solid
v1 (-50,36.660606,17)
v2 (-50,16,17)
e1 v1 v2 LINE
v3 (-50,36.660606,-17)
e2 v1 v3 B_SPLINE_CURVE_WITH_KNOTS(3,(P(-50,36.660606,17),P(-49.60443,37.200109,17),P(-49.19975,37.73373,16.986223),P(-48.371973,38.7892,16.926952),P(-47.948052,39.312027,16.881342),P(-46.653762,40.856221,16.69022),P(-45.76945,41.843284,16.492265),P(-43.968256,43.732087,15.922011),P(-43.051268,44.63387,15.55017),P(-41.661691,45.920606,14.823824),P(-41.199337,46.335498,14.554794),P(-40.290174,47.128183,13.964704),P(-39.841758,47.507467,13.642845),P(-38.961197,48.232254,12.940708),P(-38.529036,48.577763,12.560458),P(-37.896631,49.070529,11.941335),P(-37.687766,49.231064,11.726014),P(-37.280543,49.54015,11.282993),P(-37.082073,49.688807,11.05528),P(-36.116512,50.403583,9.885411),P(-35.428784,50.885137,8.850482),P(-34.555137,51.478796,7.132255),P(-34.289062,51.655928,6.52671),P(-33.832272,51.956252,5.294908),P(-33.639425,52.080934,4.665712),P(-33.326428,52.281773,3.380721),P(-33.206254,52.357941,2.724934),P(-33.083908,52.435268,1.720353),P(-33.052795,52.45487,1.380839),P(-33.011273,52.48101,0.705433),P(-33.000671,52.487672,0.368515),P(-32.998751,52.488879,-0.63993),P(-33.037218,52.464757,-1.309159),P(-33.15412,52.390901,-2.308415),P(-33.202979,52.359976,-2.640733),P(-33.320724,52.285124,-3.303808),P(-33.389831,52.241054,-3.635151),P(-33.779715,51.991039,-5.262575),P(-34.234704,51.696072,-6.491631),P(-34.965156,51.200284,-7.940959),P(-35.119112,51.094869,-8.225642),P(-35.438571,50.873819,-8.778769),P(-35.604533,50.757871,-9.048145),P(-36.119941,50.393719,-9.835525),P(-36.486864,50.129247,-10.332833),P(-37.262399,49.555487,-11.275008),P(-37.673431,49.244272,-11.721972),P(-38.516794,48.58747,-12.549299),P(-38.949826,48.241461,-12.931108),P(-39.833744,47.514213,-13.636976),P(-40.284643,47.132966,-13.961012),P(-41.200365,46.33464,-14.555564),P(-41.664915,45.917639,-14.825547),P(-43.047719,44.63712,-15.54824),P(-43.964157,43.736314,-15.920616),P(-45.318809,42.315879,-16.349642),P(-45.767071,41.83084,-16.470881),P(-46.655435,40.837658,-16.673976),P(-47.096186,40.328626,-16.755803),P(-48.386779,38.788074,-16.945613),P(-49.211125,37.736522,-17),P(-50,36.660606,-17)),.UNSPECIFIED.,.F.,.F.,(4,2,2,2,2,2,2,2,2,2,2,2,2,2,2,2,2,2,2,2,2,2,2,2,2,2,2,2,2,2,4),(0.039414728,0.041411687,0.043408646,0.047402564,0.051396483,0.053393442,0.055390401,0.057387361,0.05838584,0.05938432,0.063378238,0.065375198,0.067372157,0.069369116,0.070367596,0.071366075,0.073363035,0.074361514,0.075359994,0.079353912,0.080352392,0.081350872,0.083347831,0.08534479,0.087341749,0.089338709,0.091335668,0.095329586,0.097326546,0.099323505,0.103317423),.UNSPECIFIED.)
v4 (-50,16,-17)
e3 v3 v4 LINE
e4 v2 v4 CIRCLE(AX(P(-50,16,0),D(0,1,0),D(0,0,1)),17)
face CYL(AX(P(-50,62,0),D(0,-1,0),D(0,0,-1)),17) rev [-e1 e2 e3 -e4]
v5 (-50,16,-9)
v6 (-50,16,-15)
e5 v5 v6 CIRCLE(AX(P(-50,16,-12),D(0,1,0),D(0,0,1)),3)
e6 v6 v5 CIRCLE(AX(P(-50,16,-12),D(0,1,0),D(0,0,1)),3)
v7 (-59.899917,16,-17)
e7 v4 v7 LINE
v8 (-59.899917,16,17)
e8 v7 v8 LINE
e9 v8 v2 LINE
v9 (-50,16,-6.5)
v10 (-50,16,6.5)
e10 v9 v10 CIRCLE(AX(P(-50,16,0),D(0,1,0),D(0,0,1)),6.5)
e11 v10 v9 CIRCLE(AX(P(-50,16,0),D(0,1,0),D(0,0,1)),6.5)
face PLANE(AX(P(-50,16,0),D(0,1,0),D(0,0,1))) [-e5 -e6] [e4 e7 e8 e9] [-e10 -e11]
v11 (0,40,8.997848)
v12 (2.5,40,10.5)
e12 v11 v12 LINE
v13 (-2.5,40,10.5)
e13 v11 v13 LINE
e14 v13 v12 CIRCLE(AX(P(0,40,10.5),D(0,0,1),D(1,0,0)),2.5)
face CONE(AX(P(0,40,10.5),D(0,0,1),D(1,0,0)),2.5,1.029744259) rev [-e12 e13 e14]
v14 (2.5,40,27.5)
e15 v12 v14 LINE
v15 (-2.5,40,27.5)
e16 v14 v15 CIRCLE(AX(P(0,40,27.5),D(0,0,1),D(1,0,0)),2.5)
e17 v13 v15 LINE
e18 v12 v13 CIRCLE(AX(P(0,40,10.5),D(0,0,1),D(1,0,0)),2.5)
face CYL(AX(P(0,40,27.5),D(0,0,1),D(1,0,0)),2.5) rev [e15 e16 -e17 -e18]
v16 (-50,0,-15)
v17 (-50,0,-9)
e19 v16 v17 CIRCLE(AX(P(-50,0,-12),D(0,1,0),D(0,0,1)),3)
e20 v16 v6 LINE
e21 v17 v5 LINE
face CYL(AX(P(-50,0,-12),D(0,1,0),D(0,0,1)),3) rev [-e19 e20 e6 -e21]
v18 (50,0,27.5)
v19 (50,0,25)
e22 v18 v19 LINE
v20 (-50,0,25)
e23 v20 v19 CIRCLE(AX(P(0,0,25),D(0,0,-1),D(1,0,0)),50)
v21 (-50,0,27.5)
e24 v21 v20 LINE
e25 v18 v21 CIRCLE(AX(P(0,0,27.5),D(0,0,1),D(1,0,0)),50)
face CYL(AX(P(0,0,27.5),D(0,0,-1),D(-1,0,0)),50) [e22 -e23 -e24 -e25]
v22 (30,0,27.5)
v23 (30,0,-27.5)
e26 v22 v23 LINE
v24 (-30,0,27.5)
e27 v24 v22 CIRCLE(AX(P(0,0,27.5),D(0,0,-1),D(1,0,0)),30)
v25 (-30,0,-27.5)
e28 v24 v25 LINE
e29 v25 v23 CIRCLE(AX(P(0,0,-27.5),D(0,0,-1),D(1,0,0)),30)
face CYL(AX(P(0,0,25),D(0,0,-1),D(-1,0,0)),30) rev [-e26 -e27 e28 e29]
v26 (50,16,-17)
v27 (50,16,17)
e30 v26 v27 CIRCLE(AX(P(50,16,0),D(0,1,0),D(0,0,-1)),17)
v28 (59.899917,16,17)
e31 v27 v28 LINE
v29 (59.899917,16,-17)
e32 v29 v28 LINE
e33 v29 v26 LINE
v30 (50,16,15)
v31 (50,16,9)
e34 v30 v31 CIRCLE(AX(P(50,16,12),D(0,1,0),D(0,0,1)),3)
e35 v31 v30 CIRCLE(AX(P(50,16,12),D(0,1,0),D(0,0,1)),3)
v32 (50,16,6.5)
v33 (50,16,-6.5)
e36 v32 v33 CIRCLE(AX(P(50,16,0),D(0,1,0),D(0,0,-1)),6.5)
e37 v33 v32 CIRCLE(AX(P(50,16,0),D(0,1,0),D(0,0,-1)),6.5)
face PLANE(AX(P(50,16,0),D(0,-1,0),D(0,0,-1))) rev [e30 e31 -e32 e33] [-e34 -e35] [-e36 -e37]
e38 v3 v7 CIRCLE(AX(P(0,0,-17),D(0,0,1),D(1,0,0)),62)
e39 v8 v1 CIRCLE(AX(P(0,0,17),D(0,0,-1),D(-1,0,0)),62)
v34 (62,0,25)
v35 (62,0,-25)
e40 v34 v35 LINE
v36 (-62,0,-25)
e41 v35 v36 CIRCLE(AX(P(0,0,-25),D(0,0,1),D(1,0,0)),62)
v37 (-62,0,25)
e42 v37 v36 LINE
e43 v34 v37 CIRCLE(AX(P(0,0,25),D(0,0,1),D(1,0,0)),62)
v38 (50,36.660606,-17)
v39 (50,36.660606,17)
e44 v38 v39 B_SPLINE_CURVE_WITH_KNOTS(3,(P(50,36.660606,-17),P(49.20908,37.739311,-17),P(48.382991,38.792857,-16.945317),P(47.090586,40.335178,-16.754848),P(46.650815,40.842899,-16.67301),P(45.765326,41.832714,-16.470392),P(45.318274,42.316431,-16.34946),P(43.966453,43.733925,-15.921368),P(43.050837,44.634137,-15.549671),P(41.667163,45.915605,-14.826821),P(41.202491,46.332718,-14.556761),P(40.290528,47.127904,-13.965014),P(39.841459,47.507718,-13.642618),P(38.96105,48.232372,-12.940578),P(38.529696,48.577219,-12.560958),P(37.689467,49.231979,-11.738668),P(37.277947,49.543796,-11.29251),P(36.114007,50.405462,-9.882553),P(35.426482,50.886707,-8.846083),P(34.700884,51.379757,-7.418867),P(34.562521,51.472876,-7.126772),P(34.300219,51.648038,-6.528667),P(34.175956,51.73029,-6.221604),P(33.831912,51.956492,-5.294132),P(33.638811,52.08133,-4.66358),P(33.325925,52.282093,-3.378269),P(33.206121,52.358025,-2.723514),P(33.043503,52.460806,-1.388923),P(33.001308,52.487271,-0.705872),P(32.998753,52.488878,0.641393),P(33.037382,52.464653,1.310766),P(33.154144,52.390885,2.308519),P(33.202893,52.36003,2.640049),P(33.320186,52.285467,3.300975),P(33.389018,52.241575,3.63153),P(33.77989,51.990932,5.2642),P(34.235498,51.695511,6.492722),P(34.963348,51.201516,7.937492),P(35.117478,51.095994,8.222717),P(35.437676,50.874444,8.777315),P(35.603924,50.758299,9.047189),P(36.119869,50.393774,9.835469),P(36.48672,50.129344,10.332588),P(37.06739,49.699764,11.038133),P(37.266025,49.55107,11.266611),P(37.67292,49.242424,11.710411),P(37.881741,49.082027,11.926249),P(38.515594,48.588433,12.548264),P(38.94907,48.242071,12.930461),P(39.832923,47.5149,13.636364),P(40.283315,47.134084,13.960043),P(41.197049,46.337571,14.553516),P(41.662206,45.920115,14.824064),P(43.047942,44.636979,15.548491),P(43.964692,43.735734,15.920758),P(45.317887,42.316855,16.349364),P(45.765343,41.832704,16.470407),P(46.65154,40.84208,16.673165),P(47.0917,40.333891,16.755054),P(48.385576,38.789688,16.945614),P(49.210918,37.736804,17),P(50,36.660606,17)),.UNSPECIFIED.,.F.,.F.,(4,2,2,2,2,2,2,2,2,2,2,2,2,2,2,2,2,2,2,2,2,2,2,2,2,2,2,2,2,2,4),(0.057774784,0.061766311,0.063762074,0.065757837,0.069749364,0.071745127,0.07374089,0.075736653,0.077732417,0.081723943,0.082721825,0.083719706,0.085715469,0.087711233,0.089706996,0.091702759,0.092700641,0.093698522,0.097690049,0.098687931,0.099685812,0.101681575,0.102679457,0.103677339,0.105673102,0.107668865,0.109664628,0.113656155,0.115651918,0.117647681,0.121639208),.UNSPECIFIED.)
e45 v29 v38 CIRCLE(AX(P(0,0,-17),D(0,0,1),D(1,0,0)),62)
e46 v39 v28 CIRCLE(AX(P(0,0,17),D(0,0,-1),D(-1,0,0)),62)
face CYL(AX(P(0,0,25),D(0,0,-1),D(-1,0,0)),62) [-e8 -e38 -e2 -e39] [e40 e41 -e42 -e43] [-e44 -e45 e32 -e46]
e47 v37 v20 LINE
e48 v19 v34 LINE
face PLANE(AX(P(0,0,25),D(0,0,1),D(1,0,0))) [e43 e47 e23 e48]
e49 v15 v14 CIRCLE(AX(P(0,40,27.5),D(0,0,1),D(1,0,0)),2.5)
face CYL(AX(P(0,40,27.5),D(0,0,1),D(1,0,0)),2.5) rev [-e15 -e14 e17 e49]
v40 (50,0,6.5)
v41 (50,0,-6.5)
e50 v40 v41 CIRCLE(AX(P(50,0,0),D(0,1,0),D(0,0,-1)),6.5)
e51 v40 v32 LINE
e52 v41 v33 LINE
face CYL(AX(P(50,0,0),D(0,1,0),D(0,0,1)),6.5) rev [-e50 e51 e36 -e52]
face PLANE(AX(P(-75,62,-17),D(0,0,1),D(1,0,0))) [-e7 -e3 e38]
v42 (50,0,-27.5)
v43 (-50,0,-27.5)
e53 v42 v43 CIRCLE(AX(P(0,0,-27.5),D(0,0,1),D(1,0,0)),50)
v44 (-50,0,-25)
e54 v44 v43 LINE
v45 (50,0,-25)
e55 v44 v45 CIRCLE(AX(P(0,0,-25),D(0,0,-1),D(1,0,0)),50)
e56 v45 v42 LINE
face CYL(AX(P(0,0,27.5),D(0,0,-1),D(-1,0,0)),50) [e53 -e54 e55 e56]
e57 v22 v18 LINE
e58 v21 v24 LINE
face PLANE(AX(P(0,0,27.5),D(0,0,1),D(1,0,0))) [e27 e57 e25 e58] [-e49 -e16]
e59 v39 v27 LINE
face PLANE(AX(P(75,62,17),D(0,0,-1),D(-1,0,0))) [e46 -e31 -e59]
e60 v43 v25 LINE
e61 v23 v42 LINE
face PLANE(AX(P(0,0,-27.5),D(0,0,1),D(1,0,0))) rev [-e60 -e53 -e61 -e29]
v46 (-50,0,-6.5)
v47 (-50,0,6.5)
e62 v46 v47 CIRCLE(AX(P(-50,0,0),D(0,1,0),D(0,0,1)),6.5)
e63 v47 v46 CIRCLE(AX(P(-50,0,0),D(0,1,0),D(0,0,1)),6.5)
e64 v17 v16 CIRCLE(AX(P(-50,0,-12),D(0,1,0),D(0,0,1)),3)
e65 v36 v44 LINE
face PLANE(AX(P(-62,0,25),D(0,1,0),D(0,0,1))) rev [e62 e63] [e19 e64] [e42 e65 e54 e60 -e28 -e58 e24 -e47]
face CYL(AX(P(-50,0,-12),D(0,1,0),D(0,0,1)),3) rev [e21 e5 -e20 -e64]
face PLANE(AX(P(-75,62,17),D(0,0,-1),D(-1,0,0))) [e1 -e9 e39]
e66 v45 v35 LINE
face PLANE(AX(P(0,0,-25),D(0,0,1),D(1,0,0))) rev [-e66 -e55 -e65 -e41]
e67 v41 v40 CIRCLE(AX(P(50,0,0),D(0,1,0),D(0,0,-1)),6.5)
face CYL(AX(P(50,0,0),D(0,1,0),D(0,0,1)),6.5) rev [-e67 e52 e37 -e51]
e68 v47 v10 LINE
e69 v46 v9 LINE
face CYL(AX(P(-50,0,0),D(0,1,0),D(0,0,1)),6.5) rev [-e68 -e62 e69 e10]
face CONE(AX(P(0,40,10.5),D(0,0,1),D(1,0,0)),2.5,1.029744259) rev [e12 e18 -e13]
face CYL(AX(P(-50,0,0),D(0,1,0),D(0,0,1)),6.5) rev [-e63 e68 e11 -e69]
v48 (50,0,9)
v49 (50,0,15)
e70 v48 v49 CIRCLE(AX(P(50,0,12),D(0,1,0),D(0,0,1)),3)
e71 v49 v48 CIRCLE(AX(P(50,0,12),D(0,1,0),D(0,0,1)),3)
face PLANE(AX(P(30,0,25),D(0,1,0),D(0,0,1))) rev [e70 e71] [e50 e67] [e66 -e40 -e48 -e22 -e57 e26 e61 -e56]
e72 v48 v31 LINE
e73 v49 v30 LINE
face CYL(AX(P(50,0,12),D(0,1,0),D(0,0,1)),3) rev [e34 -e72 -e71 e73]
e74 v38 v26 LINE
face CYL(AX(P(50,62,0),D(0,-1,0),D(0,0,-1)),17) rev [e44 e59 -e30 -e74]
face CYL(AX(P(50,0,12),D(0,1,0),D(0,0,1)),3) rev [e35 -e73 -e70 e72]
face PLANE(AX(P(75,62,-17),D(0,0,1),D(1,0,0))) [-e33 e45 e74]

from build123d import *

# Parameters (mm, degrees)
BOSS_EXTRUDE1_DEPTH   = 25
BOSS_EXTRUDE2_DEPTH   = 27.5
CUT_EXTRUDE1_DEPTH    = 82.952730278
SKETCH4_R             = 6.5
SKETCH4_R_2           = 3
CUT_EXTRUDE2_DEPTH    = 82.95273041
M6_TAPPED_HOLE1_D     = 5
M6_TAPPED_HOLE1_DEPTH = 17
M6_TAPPED_HOLE1_TIP   = 1.502151548


with BuildPart() as part:
    # Sketch1 → Boss-Extrude1 (new, symmetric)
    with BuildSketch(Plane.XY):
        with BuildLine():
            Line((-62, 0), (-30, 0))
            ThreePointArc((-30, 0), (0, 30), (30, 0))
            Line((30, 0), (62, 0))
            ThreePointArc((62, 0), (0, 62), (-62, 0))
        make_face()
    extrude(amount=BOSS_EXTRUDE1_DEPTH, both=True)

    # Sketch2 → Boss-Extrude2 (add, symmetric)
    with BuildSketch(Plane.XY):
        with BuildLine():
            Line((-50, 0), (-30, 0))
            ThreePointArc((-30, 0), (0, 30), (30, 0))
            Line((30, 0), (50, 0))
            ThreePointArc((50, 0), (0, 50), (-50, 0))
        make_face()
    extrude(amount=BOSS_EXTRUDE2_DEPTH, both=True)

    # Sketch3 → Cut-Extrude1 (cut, through all)
    with BuildSketch(Plane(origin=(0, 16, 0), x_dir=(1, 0, 0), z_dir=(0, 1, 0))):
        with BuildLine():
            Line((-75, 17), (-50, 17))
            ThreePointArc((-50, 17), (-33, 0), (-50, -17))
            Line((-50, -17), (-75, -17))
            Line((-75, -17), (-75, 17))
        make_face()
        with BuildLine():
            Line((75, -17), (50, -17))
            ThreePointArc((50, -17), (33, 0), (50, 17))
            Line((50, 17), (75, 17))
            Line((75, 17), (75, -17))
        make_face()
    extrude(amount=CUT_EXTRUDE1_DEPTH, mode=Mode.SUBTRACT)

    # Sketch4 → Cut-Extrude2 (cut, through all)
    with BuildSketch(Plane(origin=(0, 16, 0), x_dir=(1, 0, 0), z_dir=(0, 1, 0))):
        with Locations(Location((-50, 0, 0), (0, 0, 270))):
            Circle(SKETCH4_R)
        with Locations(Location((-50, 12, 0), (0, 0, 270))):
            Circle(SKETCH4_R_2)
        with Locations(Location((50, 0, 0), (0, 0, 90))):
            Circle(SKETCH4_R)
        with Locations(Location((50, -12, 0), (0, 0, 270))):
            Circle(SKETCH4_R_2)
    extrude(amount=-CUT_EXTRUDE2_DEPTH, mode=Mode.SUBTRACT)

    # M6 Tapped Hole1
    with Locations(Plane.XY.offset(27.5)):
        with Locations((0, 40)):
            Hole(M6_TAPPED_HOLE1_D / 2, depth=M6_TAPPED_HOLE1_DEPTH)
            with Locations((0, 0, -(M6_TAPPED_HOLE1_DEPTH + M6_TAPPED_HOLE1_TIP / 2))):  # 118° drill point
                Cone(0, M6_TAPPED_HOLE1_D / 2, M6_TAPPED_HOLE1_TIP, mode=Mode.SUBTRACT)


solid = part.part
